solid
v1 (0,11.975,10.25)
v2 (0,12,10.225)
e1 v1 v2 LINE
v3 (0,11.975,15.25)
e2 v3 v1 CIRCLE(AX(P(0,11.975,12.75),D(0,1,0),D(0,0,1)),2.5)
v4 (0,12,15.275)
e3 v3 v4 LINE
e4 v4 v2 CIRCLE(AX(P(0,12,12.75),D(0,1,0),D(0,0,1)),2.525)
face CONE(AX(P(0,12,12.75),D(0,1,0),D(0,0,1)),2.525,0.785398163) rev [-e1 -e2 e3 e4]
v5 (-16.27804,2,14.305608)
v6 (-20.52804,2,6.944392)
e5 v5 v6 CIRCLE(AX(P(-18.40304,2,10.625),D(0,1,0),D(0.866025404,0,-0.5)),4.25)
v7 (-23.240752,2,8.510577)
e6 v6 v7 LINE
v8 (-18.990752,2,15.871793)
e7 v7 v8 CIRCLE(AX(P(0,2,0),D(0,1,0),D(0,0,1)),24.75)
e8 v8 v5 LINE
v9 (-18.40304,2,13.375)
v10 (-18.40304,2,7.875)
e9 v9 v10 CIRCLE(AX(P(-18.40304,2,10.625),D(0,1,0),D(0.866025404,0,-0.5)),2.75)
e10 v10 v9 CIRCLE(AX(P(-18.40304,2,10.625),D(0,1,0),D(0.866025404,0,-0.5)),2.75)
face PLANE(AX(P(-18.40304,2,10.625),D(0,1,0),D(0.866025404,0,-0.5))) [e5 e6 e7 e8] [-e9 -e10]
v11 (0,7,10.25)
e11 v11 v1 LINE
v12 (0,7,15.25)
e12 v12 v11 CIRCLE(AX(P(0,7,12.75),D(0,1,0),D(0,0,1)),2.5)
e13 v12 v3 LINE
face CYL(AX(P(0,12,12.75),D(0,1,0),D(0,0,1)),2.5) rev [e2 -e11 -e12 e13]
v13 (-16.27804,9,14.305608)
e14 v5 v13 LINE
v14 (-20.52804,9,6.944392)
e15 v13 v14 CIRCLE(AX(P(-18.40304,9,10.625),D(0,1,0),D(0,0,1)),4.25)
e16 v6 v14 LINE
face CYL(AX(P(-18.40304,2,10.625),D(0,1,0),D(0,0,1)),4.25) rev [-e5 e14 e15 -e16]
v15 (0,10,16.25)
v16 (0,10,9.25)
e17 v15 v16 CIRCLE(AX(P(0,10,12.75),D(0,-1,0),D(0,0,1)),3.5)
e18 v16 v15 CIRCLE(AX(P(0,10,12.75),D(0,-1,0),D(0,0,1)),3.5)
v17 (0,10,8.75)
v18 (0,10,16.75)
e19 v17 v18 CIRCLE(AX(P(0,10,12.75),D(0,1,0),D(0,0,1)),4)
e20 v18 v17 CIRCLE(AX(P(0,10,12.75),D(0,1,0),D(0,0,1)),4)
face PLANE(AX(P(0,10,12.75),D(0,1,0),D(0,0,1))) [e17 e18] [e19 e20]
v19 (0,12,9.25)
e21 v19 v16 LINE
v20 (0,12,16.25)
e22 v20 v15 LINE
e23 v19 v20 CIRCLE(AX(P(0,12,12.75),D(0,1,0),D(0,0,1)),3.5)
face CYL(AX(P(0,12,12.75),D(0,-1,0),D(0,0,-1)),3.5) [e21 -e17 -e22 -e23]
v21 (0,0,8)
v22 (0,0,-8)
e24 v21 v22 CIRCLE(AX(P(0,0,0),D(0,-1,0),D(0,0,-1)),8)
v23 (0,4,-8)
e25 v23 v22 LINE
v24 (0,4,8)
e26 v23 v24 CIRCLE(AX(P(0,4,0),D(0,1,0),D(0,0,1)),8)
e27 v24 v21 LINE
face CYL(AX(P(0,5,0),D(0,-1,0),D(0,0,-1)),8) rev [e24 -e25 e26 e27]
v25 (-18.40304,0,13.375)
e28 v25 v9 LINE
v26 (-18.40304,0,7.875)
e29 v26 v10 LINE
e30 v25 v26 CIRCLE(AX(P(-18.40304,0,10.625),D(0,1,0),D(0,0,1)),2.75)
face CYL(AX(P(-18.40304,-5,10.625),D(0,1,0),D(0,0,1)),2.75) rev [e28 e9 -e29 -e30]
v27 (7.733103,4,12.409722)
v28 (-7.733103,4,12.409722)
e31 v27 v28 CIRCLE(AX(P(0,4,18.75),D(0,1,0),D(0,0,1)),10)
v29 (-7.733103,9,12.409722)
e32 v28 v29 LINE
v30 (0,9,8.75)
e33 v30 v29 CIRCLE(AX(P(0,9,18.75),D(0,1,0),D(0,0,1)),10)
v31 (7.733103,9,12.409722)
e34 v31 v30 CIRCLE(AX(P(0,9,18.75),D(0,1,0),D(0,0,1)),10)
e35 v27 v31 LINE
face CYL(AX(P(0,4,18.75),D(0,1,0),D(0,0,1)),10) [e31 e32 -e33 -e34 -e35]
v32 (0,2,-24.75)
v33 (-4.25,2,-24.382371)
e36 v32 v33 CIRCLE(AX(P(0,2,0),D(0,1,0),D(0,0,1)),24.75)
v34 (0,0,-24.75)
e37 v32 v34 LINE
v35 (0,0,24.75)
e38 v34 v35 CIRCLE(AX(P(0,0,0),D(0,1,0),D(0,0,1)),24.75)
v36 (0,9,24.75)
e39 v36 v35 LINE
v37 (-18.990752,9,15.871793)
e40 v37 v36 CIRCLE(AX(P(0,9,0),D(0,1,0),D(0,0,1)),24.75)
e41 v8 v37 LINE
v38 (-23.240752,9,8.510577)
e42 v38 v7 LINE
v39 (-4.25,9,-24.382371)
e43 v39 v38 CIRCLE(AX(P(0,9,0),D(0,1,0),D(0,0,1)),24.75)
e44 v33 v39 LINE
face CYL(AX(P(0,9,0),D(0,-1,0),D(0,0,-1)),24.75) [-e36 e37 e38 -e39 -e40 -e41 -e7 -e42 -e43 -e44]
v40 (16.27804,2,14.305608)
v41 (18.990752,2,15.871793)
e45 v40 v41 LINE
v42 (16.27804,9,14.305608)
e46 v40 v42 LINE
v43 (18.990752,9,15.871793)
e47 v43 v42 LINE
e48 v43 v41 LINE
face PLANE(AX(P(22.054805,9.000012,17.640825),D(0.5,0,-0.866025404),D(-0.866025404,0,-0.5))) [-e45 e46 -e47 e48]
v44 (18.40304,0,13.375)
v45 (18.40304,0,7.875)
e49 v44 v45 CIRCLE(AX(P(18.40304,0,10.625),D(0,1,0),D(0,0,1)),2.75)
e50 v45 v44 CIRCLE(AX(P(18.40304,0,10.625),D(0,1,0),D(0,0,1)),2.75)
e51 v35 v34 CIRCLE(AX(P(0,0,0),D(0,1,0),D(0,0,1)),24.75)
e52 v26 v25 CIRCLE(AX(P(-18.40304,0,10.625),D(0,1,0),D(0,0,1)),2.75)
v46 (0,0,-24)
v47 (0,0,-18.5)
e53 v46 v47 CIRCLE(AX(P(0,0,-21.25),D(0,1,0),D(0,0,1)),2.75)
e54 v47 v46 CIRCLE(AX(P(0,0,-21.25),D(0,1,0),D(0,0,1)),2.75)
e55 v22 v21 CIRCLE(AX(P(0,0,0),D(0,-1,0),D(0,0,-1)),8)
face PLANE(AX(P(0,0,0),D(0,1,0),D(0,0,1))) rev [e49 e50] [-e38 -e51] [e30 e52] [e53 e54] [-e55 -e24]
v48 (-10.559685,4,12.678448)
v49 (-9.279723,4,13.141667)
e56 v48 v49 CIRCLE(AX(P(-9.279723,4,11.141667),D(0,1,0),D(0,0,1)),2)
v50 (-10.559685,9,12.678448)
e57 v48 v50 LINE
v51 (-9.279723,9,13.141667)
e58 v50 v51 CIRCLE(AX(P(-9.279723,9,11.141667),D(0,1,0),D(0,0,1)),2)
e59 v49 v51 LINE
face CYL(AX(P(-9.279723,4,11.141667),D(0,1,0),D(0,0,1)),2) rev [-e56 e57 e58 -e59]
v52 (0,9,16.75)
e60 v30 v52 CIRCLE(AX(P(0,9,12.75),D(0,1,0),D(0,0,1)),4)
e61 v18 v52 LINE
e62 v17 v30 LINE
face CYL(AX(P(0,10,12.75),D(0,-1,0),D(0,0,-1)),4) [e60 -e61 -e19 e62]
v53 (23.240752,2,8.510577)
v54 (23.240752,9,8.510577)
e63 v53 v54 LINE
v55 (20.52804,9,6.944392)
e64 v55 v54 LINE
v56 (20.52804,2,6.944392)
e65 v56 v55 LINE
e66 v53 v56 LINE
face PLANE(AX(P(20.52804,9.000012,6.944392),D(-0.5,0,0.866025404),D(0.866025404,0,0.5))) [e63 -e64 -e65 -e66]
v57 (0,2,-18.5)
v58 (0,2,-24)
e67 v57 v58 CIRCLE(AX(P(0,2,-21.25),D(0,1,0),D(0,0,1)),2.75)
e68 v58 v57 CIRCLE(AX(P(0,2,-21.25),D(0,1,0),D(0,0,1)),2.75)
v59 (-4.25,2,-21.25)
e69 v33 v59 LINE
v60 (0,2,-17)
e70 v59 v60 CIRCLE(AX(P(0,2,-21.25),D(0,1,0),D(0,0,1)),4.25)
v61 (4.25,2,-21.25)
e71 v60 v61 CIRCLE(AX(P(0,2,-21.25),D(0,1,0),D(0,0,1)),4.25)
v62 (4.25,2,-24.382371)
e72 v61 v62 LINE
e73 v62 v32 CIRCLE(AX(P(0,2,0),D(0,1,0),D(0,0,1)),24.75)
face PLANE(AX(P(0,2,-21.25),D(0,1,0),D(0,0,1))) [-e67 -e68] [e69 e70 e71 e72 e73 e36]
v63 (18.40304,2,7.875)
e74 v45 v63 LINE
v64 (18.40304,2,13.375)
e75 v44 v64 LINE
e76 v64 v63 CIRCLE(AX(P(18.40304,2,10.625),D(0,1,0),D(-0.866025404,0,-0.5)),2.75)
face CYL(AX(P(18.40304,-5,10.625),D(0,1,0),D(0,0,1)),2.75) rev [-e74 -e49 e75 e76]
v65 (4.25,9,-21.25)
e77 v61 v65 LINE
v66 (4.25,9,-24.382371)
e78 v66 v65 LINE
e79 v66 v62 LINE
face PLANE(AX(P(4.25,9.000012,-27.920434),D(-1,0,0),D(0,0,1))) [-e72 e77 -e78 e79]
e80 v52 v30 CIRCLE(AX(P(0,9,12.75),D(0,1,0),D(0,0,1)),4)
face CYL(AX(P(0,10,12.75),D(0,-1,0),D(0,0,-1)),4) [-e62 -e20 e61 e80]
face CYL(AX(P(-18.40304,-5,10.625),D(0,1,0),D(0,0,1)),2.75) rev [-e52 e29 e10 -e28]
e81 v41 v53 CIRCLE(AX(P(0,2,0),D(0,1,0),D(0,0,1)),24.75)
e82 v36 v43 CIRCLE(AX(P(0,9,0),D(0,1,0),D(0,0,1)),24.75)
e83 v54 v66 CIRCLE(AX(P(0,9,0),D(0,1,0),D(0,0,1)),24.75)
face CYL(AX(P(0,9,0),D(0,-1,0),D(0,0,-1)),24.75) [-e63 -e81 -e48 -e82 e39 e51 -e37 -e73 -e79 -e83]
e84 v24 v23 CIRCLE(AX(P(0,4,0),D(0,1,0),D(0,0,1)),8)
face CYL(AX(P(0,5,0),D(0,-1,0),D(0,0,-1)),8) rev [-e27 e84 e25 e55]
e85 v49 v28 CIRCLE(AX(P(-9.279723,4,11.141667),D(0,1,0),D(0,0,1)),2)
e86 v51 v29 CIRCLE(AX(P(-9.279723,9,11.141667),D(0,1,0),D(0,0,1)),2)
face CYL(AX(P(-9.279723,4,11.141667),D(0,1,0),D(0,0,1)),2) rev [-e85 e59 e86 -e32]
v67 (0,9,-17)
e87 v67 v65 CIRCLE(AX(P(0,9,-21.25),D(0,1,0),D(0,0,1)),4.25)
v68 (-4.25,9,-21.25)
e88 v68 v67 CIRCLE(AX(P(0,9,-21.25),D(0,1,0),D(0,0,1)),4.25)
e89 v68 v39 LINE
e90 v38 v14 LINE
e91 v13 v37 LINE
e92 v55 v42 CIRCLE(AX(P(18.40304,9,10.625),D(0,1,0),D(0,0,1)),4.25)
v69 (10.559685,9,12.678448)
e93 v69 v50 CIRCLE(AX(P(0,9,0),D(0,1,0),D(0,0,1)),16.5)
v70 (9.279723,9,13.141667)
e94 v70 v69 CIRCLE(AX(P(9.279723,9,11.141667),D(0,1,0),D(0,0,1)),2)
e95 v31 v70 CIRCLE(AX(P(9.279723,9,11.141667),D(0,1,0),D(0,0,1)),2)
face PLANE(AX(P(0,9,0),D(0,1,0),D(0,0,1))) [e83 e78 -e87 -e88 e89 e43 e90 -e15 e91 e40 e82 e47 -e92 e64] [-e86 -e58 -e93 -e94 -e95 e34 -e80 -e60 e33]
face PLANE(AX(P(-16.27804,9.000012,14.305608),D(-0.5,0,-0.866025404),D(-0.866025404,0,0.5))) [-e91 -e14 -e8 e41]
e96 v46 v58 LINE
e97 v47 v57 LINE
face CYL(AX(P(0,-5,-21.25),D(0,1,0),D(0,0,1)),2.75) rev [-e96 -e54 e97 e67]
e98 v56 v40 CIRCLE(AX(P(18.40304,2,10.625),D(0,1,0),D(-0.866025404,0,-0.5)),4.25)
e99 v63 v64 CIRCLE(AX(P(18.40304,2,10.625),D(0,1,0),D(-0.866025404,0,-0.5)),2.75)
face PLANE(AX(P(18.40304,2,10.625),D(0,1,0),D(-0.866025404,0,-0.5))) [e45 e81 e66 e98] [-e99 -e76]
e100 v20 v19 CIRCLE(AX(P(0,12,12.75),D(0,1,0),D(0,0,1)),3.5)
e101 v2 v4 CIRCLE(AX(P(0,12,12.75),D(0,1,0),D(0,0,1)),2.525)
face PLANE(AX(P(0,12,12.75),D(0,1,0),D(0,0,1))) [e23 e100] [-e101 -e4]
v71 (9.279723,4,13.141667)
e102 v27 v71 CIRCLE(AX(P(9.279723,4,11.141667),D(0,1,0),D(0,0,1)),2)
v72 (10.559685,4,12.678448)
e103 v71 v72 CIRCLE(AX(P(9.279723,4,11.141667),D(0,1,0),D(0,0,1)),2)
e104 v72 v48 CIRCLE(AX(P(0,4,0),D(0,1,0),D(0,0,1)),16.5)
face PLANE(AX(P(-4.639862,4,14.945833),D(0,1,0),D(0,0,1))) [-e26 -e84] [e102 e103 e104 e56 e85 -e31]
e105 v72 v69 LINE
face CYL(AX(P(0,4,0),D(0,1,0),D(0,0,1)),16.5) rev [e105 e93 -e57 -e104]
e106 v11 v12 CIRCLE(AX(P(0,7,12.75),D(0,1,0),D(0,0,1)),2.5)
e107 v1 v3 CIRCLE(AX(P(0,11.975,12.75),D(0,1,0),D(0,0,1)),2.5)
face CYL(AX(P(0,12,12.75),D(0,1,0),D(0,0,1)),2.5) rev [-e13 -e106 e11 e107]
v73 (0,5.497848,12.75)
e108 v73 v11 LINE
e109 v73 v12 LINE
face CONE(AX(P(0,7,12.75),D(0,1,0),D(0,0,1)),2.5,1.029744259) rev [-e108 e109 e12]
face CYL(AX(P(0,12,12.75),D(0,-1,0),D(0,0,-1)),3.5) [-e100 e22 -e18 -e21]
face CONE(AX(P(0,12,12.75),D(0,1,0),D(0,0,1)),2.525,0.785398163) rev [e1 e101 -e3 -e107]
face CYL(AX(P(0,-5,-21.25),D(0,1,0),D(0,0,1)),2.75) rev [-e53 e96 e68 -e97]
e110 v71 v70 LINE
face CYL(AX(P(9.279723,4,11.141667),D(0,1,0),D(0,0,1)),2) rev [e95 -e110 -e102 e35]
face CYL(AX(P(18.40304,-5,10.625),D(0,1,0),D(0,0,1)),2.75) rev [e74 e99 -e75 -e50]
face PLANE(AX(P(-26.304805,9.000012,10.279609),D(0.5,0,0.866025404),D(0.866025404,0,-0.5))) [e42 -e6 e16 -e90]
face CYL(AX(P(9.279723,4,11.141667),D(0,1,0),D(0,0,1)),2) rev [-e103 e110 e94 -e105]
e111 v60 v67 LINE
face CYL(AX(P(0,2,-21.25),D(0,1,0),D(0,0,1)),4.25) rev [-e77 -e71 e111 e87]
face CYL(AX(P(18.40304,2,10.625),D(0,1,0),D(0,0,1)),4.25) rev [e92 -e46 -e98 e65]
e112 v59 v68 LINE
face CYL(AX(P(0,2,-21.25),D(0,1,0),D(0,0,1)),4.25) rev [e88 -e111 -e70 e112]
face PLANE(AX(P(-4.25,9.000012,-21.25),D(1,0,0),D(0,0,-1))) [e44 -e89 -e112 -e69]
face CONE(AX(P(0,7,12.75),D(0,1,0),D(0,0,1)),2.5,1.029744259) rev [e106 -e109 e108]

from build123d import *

# Parameters (mm, degrees)
SKETCH1_R                              = 24.75
BOSS_EXTRUDE1_DEPTH                    = 9
CUT_EXTRUDE1_START                     = -7
CUT_EXTRUDE1_DEPTH                     = 44.140351409
SKETCH3_R                              = 2.75
CUT_EXTRUDE2_DEPTH                     = 7
CIRPATTERN1_COUNT                      = 3
SKETCH5_R                              = 4
BOSS_EXTRUDE2_DEPTH                    = 1
SKETCH6_R                              = 3.5
BOSS_EXTRUDE3_DEPTH                    = 3
F_5_0MM_BLIND_DOWEL_HOLE_1_D           = 5
F_5_0MM_BLIND_DOWEL_HOLE_1_DEPTH       = 5
F_5_0MM_BLIND_DOWEL_HOLE_1_CSINK_D     = 5.05
F_5_0MM_BLIND_DOWEL_HOLE_1_CSINK_ANGLE = 90
F_5_0MM_BLIND_DOWEL_HOLE_1_TIP         = 1.502151548
CUT_EXTRUDE3_START                     = 7
CUT_EXTRUDE3_DEPTH                     = 5
SKETCH9_R                              = 8
CUT_EXTRUDE4_DEPTH                     = 5


with BuildPart() as part:
    # Sketch1 → Boss-Extrude1 (new body)
    with BuildSketch(Plane(origin=(0, 0, 0), x_dir=(1, 0, 0), z_dir=(0, 1, 0))):
        with Locations(Location((0, 0, 0), (0, 0, 270))):
            Circle(SKETCH1_R)
    extrude(amount=BOSS_EXTRUDE1_DEPTH)

    # Sketch2 → Cut-Extrude1 (cut)
    with BuildSketch(Plane(origin=(0, 9, 0), x_dir=(1, 0, 0), z_dir=(0, 1, 0)).offset(CUT_EXTRUDE1_START)):
        with BuildLine():
            Line((-4.25, 21.25), (-4.25, 27.920433859))
            Line((-4.25, 27.920433859), (4.25, 27.920433859))
            Line((4.25, 27.920433859), (4.25, 21.25))
            ThreePointArc((4.25, 21.25), (0, 17), (-4.25, 21.25))
        make_face()
    cut_extrude1 = extrude(amount=CUT_EXTRUDE1_DEPTH, mode=Mode.SUBTRACT)

    # Sketch3 → Cut-Extrude2 (cut)
    with BuildSketch(Plane(origin=(0, 2, 0), x_dir=(1, 0, 0), z_dir=(0, 1, 0))):
        with Locations(Location((0, 21.25, 0), (0, 0, 270))):
            Circle(SKETCH3_R)
    cut_extrude2 = extrude(amount=-CUT_EXTRUDE2_DEPTH, mode=Mode.SUBTRACT)

    # CirPattern1: Cut-Extrude1, Cut-Extrude2 ×3 about axis
    cirpattern1_axis = Axis((0, 0, 0), (0, 1, 0))
    add([cut_extrude1.rotate(cirpattern1_axis, i * 360 / CIRPATTERN1_COUNT) for i in range(1, CIRPATTERN1_COUNT)], mode=Mode.SUBTRACT)
    add([cut_extrude2.rotate(cirpattern1_axis, i * 360 / CIRPATTERN1_COUNT) for i in range(1, CIRPATTERN1_COUNT)], mode=Mode.SUBTRACT)

    # Sketch5 → Boss-Extrude2 (add)
    with BuildSketch(Plane(origin=(0, 9, 0), x_dir=(1, 0, 0), z_dir=(0, 1, 0))):
        with Locations(Location((0, -12.75, 0), (0, 0, 270))):
            Circle(SKETCH5_R)
    extrude(amount=BOSS_EXTRUDE2_DEPTH)

    # Sketch6 → Boss-Extrude3 (add)
    with BuildSketch(Plane(origin=(0, 9, 0), x_dir=(1, 0, 0), z_dir=(0, 1, 0))):
        with Locations(Location((0, -12.75, 0), (0, 0, 270))):
            Circle(SKETCH6_R)
    extrude(amount=BOSS_EXTRUDE3_DEPTH)

    # Ø5.0mm blind dowel hole 1
    with Locations(Plane(origin=(0, 12, 0), x_dir=(1, 0, 0), z_dir=(0, 1, 0))):
        with Locations((0, -12.75)):
            CounterSinkHole(F_5_0MM_BLIND_DOWEL_HOLE_1_D / 2, F_5_0MM_BLIND_DOWEL_HOLE_1_CSINK_D / 2, depth=F_5_0MM_BLIND_DOWEL_HOLE_1_DEPTH, counter_sink_angle=F_5_0MM_BLIND_DOWEL_HOLE_1_CSINK_ANGLE)
            with Locations((0, 0, -(F_5_0MM_BLIND_DOWEL_HOLE_1_DEPTH + F_5_0MM_BLIND_DOWEL_HOLE_1_TIP / 2))):  # 118° drill point
                Cone(0, F_5_0MM_BLIND_DOWEL_HOLE_1_D / 2, F_5_0MM_BLIND_DOWEL_HOLE_1_TIP, mode=Mode.SUBTRACT)

    # Sketch4 → Cut-Extrude3 (cut)
    with BuildSketch(Plane(origin=(0, 2, 0), x_dir=(1, 0, 0), z_dir=(0, 1, 0)).offset(CUT_EXTRUDE3_START)):
        with BuildLine():
            ThreePointArc((10.559685096, -12.678448276), (0, 16.5), (-10.559685096, -12.678448276))
            ThreePointArc((-10.559685096, -12.678448276), (-9.090434755, -13.132688982), (-7.733102721, -12.409722222))
            ThreePointArc((-7.733102721, -12.409722222), (0, -8.75), (7.733102721, -12.409722222))
            ThreePointArc((7.733102721, -12.409722222), (9.090434755, -13.132688982), (10.559685096, -12.678448276))
        make_face()
    extrude(amount=-CUT_EXTRUDE3_DEPTH, mode=Mode.SUBTRACT)

    # Sketch9 → Cut-Extrude4 (cut)
    with BuildSketch(Plane.XZ):
        with Locations(Location((0, 0, 0), (0, 0, 270))):
            Circle(SKETCH9_R)
    extrude(amount=-CUT_EXTRUDE4_DEPTH, mode=Mode.SUBTRACT)


solid = part.part
